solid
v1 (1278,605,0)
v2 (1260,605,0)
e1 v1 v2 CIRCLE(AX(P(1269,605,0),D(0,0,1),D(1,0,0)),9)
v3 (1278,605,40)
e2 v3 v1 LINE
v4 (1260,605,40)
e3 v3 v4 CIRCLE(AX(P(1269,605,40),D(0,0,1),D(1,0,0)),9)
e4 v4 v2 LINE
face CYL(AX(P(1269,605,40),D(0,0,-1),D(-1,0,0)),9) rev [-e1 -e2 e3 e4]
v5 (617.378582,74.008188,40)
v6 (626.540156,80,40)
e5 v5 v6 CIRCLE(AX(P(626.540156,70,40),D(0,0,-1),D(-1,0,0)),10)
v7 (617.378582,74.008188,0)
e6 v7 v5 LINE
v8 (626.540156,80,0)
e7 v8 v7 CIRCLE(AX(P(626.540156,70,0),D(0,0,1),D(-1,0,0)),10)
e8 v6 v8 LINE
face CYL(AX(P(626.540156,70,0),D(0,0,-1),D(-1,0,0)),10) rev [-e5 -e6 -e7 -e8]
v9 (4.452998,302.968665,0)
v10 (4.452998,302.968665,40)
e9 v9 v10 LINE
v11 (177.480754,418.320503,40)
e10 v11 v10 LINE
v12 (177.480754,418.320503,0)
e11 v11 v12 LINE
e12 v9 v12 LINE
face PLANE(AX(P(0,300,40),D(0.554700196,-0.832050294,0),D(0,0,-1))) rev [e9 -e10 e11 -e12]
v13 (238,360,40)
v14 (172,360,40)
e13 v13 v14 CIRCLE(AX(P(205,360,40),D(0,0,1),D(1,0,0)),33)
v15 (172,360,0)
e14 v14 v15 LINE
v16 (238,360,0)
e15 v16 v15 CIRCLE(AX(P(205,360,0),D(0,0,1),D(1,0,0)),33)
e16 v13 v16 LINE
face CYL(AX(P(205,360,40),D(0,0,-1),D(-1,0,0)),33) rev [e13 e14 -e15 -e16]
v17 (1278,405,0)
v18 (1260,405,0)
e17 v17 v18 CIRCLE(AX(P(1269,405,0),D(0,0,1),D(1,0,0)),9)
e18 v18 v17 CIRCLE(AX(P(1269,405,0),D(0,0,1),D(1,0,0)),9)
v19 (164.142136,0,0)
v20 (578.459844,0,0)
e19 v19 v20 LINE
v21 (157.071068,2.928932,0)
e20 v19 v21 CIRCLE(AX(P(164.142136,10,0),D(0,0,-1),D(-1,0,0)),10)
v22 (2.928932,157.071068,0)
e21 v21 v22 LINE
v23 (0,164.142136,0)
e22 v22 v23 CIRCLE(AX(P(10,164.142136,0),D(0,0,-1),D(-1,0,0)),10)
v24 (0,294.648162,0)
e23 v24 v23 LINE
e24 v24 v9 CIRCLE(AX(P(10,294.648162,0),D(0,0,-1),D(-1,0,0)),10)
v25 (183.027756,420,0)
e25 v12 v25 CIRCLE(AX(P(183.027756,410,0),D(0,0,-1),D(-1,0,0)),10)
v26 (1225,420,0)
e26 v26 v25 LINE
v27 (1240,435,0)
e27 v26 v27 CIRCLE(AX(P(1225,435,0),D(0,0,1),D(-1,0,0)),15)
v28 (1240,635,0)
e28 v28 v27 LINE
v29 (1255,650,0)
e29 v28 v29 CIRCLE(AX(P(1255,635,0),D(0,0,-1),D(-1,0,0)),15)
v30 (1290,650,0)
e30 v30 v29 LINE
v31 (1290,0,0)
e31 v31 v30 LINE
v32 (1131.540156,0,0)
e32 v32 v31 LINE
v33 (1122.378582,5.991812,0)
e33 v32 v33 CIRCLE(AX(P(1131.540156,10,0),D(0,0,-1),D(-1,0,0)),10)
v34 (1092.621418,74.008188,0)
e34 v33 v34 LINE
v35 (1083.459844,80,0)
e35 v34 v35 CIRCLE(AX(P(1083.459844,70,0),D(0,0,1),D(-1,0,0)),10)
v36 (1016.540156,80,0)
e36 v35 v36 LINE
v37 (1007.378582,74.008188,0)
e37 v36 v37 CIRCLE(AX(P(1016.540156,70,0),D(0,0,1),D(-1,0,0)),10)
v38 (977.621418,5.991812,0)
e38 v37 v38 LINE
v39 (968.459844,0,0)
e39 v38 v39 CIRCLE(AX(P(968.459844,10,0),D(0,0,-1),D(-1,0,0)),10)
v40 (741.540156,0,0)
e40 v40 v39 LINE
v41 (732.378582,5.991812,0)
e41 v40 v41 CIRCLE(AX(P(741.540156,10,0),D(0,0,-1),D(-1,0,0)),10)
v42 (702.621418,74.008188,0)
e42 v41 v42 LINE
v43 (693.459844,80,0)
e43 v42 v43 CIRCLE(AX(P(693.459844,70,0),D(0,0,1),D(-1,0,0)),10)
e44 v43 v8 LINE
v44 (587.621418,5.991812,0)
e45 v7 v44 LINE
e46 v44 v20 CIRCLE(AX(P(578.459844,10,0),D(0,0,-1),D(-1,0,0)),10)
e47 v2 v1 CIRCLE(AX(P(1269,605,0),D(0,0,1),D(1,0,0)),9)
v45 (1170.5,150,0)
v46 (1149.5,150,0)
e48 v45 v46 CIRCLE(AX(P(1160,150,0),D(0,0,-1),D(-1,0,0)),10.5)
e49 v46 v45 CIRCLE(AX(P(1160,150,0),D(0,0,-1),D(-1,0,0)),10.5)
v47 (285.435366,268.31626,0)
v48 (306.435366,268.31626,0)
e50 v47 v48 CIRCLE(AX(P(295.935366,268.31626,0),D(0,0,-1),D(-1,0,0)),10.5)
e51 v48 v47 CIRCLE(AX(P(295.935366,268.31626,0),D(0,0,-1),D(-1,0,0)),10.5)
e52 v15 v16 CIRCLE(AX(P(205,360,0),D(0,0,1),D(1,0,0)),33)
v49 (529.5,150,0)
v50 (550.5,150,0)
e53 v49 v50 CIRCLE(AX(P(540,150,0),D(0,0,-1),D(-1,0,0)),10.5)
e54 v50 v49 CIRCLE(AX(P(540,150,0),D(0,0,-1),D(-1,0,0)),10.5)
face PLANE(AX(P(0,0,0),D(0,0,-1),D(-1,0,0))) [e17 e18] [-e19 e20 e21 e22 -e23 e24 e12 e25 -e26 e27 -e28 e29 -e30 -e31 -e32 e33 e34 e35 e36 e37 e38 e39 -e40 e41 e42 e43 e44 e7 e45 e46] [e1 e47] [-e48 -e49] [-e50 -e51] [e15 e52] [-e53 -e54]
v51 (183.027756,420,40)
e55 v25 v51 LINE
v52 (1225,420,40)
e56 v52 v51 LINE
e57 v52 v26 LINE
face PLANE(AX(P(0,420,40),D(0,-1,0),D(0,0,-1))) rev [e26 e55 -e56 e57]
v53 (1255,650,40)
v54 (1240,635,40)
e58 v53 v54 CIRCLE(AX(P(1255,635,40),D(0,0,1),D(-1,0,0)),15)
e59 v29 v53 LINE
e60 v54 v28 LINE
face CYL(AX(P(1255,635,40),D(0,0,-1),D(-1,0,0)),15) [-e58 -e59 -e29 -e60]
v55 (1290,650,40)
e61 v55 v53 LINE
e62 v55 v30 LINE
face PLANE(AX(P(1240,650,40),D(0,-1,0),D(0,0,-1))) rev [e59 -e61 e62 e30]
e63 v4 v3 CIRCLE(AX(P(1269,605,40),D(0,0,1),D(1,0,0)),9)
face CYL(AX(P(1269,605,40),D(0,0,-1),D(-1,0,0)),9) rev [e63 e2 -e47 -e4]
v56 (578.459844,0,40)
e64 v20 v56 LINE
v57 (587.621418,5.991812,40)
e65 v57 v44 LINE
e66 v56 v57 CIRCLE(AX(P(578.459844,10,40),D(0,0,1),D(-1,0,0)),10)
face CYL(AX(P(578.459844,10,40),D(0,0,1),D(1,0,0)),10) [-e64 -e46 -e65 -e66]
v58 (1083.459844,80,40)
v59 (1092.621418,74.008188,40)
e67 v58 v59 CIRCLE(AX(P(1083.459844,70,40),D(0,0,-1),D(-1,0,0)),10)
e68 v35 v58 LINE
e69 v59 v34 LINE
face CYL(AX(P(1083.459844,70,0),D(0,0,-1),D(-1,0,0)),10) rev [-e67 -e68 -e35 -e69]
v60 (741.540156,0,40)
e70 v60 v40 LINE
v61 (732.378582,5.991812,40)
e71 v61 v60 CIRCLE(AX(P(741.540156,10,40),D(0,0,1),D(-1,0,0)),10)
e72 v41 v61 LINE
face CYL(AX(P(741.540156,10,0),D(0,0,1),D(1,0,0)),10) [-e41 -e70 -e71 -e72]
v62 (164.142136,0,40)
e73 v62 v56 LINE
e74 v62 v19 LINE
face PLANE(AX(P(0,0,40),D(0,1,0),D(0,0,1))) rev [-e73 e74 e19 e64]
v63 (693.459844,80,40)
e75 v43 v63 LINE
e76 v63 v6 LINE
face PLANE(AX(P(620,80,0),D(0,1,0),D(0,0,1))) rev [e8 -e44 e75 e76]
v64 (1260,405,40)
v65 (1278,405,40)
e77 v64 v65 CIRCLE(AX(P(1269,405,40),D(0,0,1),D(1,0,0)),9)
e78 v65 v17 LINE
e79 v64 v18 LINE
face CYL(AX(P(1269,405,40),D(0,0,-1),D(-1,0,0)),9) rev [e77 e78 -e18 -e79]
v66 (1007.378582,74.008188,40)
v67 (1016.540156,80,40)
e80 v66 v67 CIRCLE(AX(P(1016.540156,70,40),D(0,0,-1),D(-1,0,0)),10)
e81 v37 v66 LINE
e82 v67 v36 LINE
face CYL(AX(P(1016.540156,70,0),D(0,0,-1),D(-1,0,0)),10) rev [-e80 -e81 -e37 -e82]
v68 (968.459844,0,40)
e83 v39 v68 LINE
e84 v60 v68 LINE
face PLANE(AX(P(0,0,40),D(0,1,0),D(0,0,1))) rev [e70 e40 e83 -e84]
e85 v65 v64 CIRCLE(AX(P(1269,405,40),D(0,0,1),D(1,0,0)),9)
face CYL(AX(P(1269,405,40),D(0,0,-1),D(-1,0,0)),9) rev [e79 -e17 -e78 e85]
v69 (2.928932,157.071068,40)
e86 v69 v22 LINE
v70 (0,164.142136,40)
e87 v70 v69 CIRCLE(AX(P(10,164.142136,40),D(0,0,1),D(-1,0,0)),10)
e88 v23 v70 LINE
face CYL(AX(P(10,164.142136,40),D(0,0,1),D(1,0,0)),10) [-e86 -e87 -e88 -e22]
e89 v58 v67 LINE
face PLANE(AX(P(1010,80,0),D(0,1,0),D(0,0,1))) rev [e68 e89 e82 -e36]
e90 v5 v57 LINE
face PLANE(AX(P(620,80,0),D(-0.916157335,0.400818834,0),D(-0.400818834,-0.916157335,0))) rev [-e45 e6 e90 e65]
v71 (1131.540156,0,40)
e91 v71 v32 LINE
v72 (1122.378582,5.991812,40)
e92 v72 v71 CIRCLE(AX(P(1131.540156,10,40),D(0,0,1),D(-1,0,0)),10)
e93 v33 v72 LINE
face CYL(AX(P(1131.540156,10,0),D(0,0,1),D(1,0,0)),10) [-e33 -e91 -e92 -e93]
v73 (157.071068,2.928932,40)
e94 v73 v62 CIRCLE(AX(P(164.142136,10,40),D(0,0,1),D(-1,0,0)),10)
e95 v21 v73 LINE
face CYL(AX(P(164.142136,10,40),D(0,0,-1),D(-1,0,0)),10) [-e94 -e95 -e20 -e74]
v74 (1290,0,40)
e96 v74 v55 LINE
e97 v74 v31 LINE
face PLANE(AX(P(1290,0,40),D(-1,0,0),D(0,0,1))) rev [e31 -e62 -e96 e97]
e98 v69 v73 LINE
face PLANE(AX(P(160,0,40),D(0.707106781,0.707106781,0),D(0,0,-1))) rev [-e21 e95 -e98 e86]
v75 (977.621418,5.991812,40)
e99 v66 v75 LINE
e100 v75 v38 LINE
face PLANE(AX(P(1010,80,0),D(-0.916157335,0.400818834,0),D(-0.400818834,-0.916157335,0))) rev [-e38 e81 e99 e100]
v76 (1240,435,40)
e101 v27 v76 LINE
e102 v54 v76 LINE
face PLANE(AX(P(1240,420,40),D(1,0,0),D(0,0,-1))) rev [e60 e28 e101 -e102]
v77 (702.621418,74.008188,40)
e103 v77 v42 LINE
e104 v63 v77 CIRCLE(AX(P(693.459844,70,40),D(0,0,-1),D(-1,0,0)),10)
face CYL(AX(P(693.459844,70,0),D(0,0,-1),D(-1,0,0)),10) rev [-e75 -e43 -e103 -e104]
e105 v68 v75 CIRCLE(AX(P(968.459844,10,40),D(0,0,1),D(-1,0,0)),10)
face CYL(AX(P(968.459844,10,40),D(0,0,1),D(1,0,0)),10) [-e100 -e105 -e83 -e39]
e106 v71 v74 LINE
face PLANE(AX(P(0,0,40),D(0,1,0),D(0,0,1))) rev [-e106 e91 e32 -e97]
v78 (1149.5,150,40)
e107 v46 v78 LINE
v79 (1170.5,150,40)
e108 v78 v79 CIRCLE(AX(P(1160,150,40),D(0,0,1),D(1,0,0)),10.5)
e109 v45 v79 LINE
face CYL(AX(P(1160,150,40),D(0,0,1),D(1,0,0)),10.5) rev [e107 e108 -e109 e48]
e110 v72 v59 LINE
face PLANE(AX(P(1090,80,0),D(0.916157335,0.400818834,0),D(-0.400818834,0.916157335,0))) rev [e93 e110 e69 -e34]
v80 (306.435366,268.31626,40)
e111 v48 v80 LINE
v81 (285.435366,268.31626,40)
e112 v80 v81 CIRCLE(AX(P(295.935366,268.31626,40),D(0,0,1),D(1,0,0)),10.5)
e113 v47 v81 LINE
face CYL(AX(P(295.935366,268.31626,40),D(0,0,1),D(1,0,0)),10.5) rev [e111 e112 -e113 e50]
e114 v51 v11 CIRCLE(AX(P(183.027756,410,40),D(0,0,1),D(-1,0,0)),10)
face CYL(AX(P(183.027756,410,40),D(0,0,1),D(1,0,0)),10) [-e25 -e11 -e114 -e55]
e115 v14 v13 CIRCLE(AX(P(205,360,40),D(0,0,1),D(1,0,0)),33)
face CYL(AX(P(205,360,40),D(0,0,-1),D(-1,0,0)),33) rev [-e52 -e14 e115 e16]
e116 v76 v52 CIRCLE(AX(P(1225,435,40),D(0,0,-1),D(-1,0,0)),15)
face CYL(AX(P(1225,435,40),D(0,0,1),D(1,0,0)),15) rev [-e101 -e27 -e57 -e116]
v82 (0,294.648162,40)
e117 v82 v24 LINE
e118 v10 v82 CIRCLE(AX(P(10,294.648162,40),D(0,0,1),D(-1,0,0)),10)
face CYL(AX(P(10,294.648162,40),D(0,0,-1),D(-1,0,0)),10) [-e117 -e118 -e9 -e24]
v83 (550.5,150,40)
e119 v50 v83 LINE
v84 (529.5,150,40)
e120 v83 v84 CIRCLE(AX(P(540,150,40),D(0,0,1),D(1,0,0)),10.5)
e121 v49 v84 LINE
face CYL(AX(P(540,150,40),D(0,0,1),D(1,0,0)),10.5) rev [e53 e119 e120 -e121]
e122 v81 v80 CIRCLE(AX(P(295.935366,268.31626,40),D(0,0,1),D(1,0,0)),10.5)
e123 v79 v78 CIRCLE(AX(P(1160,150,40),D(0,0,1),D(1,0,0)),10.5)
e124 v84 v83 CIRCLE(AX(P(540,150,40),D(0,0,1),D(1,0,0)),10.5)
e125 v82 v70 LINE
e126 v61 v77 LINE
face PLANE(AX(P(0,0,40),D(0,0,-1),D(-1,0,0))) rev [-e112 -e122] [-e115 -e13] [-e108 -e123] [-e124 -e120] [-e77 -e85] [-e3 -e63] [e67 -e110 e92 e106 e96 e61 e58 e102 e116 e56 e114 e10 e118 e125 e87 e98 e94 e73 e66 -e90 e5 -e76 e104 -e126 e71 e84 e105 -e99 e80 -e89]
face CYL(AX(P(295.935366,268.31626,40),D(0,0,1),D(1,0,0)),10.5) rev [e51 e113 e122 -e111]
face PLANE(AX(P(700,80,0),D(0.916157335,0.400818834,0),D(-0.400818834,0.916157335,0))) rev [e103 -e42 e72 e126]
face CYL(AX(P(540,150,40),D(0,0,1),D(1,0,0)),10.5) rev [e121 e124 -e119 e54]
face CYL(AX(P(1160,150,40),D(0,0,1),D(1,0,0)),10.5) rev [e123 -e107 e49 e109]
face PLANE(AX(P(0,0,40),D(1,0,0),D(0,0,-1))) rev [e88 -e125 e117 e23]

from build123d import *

# Parameters (mm, degrees)
SKETCH1_R           = 33
SKETCH1_R_2         = 9
BOSS_EXTRUDE1_DEPTH = 40
CHAMFER2_SIZE       = 180
CHAMFER2_SIZE2      = 120
CHAMFER3_SIZE       = 160
M24_TAPPED_HOLE1_D  = 21
FILLET1_R           = 15
CUT_EXTRUDE1_DEPTH  = 1446.060552365
FILLET2_R           = 10
FILLET3_R           = 10


with BuildPart() as part:
    # Sketch1 → Boss-Extrude1 (new body)
    with BuildSketch(Plane.XY):
        Polygon((1240, 420), (1240, 650), (1290, 650), (1290, 0), (0, 0), (0, 420), align=None)
        with Locations((205, 360)):
            Circle(SKETCH1_R, mode=Mode.SUBTRACT)
        with Locations((1269, 405)):
            Circle(SKETCH1_R_2, mode=Mode.SUBTRACT)
        with Locations((1269, 605)):
            Circle(SKETCH1_R_2, mode=Mode.SUBTRACT)
    extrude(amount=BOSS_EXTRUDE1_DEPTH)

    # Chamfer2
    chamfer2_edges = [part.edges().sort_by_distance(p)[0] for p in [
        (0, 420, 20),
    ]]
    chamfer2_side = [part.faces().sort_by_distance(p)[0] for p in [
        (620, 420, 20),
    ]]
    chamfer(chamfer2_edges, length=CHAMFER2_SIZE, length2=CHAMFER2_SIZE2, reference=chamfer2_side[0])

    # Chamfer3
    chamfer3_edges = [part.edges().sort_by_distance(p)[0] for p in [
        (0, 0, 20),
    ]]
    chamfer(chamfer3_edges, length=CHAMFER3_SIZE)

    # M24 Tapped Hole1 (through all)
    with Locations(Plane(origin=(540, 150, 40), x_dir=(1, 0, 0), z_dir=(0, 0, 1))):
        with Locations((0, 0), (620, 0), (-244.064633972, 118.316259911)):
            Hole(M24_TAPPED_HOLE1_D / 2)

    # Fillet1
    fillet1_edges = [part.edges().sort_by_distance(p)[0] for p in [
        (1240, 420, 20),
        (1240, 650, 20),
    ]]
    fillet(fillet1_edges, radius=FILLET1_R)

    # Sketch2 → Cut-Extrude1 (cut, through all)
    with BuildSketch(Plane.XY.offset(40)):
        Polygon((585, 0), (735, 0), (700, 80), (620, 80), align=None)
        Polygon((975, 0), (1125, 0), (1090, 80), (1010, 80), align=None)
    extrude(amount=-CUT_EXTRUDE1_DEPTH, mode=Mode.SUBTRACT)

    # Fillet2
    fillet2_edges = [part.edges().sort_by_distance(p)[0] for p in [
        (700, 80, 20),
        (735, 0, 20),
        (585, 0, 20),
        (620, 80, 20),
        (1010, 80, 20),
        (1090, 80, 20),
        (1125, 0, 20),
        (975, 0, 20),
    ]]
    fillet(fillet2_edges, radius=FILLET2_R)

    # Fillet3
    fillet3_edges = [part.edges().sort_by_distance(p)[0] for p in [
        (0, 300, 20),
        (180, 420, 20),
        (160, 0, 20),
        (0, 160, 20),
    ]]
    fillet(fillet3_edges, radius=FILLET3_R)


solid = part.part
